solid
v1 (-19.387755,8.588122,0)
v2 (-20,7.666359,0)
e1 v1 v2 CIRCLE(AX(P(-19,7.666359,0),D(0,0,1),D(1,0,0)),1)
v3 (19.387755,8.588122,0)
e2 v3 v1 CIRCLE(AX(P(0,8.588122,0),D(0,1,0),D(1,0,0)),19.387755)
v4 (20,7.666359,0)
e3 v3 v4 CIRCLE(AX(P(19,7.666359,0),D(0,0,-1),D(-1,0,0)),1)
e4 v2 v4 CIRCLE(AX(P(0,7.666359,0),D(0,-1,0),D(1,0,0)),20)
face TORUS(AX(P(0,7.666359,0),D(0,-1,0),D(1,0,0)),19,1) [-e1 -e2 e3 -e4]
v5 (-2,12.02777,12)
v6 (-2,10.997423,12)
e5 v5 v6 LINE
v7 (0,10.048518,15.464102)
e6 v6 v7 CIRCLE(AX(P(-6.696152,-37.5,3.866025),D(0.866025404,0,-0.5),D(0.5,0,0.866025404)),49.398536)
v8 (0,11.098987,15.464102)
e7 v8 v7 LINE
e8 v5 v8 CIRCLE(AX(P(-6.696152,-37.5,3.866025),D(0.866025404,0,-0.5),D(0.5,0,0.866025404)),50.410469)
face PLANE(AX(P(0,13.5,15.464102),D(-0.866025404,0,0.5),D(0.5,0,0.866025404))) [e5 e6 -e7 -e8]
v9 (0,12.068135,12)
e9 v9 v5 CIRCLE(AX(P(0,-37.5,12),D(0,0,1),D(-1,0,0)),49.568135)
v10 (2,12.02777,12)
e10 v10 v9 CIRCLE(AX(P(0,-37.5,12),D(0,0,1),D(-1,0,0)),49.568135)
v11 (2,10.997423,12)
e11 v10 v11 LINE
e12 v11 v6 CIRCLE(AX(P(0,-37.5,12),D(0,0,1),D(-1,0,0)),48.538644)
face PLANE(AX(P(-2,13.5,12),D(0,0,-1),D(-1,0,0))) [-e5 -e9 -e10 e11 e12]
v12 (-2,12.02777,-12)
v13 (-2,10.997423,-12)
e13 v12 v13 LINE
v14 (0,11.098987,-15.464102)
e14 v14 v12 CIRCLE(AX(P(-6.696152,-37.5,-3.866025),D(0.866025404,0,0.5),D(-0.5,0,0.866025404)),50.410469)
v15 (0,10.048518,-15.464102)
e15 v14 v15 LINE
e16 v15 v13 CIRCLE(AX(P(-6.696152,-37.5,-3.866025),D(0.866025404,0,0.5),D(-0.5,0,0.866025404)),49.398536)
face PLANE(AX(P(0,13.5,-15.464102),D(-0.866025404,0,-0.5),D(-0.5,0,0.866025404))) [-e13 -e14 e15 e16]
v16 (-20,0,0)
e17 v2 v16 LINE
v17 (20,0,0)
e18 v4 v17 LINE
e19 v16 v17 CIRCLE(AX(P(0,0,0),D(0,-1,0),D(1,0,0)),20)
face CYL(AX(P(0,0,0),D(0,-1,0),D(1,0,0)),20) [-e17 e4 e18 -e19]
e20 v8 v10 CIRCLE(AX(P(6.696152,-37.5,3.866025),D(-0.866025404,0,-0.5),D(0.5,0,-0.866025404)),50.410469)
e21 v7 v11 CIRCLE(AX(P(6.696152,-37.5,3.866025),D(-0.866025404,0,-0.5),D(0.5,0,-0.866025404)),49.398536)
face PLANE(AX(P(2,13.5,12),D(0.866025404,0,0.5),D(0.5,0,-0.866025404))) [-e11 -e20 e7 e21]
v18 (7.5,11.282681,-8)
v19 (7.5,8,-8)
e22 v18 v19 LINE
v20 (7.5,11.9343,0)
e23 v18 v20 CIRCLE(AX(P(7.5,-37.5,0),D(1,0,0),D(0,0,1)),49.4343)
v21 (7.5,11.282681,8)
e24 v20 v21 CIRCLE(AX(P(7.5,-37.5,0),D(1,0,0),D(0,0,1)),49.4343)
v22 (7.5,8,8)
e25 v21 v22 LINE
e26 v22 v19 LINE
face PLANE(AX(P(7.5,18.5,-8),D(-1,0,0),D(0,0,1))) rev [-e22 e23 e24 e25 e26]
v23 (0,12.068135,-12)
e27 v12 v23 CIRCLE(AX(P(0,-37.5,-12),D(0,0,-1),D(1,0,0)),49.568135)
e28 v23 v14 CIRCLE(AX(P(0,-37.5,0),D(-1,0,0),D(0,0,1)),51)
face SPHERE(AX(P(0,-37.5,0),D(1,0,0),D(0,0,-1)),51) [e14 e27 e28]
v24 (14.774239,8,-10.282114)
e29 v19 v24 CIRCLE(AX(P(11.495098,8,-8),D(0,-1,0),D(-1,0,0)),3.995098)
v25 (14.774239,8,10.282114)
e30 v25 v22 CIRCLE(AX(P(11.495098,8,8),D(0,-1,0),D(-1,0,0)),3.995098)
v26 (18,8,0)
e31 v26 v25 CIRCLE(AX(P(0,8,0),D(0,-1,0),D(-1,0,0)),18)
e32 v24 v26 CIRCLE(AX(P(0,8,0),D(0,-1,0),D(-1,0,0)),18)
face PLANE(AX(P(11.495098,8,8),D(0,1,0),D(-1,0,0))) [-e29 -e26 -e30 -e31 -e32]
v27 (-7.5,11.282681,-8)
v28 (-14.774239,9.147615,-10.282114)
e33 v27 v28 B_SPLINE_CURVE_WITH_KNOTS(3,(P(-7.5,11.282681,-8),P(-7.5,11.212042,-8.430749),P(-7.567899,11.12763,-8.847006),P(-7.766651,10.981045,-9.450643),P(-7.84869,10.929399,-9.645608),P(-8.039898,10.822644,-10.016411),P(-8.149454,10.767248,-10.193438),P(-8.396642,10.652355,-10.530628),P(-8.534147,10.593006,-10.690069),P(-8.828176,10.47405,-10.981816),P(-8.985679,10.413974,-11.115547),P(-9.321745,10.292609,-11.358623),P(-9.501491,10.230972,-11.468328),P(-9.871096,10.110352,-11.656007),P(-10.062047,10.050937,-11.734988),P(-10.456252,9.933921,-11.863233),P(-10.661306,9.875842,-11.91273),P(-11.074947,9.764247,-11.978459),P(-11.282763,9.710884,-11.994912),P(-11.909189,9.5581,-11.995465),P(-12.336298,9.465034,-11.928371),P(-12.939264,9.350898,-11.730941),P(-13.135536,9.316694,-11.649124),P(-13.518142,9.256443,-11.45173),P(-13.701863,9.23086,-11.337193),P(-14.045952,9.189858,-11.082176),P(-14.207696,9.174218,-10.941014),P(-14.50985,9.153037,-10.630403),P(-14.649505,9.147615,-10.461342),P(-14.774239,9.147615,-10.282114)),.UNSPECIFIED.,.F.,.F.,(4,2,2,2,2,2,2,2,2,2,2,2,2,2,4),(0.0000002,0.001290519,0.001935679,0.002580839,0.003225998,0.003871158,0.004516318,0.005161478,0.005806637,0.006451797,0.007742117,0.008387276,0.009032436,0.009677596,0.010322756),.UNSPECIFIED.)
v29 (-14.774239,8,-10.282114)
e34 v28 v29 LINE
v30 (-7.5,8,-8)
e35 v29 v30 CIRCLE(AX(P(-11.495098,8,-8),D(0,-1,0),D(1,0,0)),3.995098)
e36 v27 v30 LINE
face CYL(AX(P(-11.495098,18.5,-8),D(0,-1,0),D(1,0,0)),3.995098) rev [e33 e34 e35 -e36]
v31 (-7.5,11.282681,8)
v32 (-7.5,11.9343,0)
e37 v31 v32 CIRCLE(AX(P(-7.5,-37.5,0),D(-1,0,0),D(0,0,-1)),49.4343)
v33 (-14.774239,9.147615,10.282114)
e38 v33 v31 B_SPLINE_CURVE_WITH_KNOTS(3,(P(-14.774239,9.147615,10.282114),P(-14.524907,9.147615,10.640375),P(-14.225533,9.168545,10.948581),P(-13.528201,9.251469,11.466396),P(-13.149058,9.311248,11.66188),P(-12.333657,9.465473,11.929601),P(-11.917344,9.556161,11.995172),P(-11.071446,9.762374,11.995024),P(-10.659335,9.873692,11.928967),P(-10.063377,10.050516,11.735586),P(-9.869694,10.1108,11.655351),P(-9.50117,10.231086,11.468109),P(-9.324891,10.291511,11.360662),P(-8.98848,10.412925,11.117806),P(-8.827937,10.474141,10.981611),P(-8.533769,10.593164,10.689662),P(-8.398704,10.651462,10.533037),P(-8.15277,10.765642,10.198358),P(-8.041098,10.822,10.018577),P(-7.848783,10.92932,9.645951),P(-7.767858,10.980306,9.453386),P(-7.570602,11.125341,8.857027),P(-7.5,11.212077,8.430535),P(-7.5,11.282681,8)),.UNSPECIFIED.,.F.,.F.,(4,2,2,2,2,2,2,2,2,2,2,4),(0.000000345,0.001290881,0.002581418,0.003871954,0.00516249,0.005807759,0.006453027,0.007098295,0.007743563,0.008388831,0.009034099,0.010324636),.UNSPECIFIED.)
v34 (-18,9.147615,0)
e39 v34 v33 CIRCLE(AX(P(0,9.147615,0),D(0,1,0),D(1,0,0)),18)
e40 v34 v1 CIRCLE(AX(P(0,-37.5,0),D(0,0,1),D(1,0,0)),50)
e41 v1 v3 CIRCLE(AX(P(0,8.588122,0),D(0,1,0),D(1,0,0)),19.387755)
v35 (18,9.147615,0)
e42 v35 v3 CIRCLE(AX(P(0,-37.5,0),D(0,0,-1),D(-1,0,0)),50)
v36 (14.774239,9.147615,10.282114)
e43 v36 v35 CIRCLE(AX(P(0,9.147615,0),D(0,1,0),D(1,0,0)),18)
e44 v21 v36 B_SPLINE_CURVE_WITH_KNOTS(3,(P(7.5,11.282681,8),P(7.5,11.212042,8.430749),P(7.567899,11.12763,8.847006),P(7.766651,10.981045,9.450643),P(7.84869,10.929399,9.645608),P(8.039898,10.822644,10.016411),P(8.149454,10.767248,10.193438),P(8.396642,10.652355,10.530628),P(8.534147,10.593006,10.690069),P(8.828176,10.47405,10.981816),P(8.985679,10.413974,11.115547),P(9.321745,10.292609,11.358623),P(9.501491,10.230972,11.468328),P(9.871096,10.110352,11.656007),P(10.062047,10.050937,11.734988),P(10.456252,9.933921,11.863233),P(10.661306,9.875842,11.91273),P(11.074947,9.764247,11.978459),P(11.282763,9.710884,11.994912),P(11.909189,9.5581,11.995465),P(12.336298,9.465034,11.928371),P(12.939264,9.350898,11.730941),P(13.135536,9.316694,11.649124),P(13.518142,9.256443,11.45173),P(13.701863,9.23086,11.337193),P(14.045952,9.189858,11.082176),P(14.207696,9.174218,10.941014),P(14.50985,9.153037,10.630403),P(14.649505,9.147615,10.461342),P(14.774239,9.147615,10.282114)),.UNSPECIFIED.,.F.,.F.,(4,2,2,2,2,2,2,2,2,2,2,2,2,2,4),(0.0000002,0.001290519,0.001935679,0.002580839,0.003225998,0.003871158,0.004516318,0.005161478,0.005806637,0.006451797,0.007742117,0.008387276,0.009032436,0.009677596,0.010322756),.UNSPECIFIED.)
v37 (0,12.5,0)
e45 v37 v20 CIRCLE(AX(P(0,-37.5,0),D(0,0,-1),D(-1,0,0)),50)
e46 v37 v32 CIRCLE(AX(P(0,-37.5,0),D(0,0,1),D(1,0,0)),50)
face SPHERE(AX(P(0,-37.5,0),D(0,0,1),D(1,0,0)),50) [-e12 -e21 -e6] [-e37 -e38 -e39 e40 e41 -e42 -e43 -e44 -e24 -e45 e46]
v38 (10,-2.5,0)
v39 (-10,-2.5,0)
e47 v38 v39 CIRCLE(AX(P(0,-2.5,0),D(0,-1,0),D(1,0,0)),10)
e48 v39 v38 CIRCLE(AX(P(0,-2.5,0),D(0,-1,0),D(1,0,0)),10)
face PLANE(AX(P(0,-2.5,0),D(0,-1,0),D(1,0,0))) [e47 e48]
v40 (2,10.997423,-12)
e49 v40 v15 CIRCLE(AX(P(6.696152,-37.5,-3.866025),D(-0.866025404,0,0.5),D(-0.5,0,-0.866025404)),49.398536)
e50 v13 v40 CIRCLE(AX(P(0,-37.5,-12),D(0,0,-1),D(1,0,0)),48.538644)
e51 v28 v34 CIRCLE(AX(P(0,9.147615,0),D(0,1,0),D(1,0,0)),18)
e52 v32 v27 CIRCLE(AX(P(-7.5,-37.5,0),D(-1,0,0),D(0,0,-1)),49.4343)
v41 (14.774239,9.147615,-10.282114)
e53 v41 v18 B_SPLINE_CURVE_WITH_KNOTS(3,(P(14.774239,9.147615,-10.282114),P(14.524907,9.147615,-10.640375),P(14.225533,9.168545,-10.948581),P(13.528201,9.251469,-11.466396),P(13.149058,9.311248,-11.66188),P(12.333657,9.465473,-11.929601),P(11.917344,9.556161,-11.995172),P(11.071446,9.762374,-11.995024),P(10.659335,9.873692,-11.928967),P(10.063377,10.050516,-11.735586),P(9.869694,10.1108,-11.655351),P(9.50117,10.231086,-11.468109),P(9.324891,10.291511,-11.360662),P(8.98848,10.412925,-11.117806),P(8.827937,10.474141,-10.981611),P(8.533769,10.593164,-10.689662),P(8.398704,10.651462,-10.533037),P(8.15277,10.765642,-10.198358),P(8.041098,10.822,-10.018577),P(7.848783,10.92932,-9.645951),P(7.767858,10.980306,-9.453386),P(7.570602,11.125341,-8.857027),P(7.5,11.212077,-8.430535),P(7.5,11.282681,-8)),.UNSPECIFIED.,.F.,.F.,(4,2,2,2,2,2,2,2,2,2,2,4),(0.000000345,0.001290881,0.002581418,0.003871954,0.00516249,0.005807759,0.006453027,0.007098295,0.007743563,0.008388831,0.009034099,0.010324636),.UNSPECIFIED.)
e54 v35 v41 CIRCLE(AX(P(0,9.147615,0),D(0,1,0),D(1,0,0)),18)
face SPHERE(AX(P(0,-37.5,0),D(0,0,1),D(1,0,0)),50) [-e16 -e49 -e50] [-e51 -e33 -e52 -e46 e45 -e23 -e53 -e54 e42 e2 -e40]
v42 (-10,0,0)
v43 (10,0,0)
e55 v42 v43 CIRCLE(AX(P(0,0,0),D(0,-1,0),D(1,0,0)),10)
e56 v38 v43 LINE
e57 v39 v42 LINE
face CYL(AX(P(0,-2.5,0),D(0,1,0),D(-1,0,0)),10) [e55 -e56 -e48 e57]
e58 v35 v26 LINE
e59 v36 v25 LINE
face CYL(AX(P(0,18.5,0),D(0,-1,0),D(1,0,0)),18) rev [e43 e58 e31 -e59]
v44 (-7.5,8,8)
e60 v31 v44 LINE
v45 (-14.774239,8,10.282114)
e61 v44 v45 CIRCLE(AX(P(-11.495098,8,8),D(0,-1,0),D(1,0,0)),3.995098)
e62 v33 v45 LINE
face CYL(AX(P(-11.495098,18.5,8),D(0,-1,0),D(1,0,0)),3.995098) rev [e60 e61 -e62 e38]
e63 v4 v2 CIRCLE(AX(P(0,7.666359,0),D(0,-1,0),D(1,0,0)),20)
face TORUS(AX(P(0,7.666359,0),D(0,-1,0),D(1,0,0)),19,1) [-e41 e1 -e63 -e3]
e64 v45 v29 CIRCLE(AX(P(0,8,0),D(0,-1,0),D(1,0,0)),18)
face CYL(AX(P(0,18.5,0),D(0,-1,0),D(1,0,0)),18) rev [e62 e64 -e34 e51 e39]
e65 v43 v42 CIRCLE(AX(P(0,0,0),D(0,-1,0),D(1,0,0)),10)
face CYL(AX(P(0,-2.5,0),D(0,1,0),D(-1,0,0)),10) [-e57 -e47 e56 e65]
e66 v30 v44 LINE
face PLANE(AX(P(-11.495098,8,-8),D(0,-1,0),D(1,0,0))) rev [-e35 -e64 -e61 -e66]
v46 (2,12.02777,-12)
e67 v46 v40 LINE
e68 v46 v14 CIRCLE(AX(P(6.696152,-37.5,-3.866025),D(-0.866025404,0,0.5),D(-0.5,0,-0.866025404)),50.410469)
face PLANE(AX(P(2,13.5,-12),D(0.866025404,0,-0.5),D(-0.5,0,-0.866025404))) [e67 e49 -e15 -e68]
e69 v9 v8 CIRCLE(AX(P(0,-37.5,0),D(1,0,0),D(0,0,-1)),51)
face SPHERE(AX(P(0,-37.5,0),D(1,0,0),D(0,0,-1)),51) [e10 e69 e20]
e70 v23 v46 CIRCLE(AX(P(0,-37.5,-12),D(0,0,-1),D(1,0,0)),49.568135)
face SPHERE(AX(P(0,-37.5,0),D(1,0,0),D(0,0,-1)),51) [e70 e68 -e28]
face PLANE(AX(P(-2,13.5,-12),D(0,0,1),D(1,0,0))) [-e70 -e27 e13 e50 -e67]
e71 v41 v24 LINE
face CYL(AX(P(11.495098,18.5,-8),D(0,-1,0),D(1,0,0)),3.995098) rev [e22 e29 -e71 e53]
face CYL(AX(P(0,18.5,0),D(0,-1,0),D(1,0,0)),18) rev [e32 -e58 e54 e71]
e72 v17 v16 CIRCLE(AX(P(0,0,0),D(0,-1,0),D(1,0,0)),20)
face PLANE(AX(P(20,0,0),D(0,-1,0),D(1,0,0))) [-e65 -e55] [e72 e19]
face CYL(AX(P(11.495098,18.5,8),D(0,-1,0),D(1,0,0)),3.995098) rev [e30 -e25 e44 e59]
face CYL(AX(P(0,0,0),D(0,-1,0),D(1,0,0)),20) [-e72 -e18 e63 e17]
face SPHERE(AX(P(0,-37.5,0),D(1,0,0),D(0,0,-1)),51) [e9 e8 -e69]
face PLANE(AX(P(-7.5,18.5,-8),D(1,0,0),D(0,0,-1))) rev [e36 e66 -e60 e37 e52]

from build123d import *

# Parameters (mm, degrees)
FILLET1_R           = 1
SKETCH2_R           = 10
BOSS_EXTRUDE1_DEPTH = 2.5
CUT_EXTRUDE1_DEPTH  = 10.5
BOSS_EXTRUDE2_DEPTH = 13.5


with BuildPart() as part:
    # Sketch1 → Revolve1 (revolve)
    with BuildSketch(Plane.XY):
        with BuildLine():
            Line((20, 8.32575695), (20, 0))
            Line((20, 0), (0, 0))
            Line((0, 0), (0, 12.5))
            ThreePointArc((0, 12.5), (10.215482184, 11.445315647), (20, 8.32575695))
        make_face()
    revolve(axis=Axis((0, 0, 0), (0, 1, 0)))

    # Fillet1
    fillet1_edges = [part.edges().sort_by_distance(p)[0] for p in [
        (-20, 8.32575695, 0),
    ]]
    fillet(fillet1_edges, radius=FILLET1_R)

    # Sketch2 → Boss-Extrude1 (add)
    with BuildSketch(Plane.XZ):
        Circle(SKETCH2_R)
    extrude(amount=BOSS_EXTRUDE1_DEPTH)

    # Sketch3 → Cut-Extrude1 (cut)
    with BuildSketch(Plane(origin=(0, 8, 0), x_dir=(-1, 0, 0), z_dir=(0, -1, 0))):
        with BuildLine():
            Line((7.5, 8), (7.5, -8))
            ThreePointArc((7.5, -8), (10.299205094, -11.811908762), (14.774238712, -10.282114106))
            ThreePointArc((14.774238712, -10.282114106), (18, 0), (14.774238712, 10.282114106))
            ThreePointArc((14.774238712, 10.282114106), (10.299205094, 11.811908762), (7.5, 8))
        make_face()
        with BuildLine():
            Line((-7.5, 8), (-7.5, -8))
            ThreePointArc((-7.5, -8), (-10.299205094, -11.811908762), (-14.774238712, -10.282114106))
            ThreePointArc((-14.774238712, -10.282114106), (-18, 0), (-14.774238712, 10.282114106))
            ThreePointArc((-14.774238712, 10.282114106), (-10.299205094, 11.811908762), (-7.5, 8))
        make_face()
    extrude(amount=-CUT_EXTRUDE1_DEPTH, mode=Mode.SUBTRACT)

    # Sketch5 → Boss-Extrude2 (add)
    with BuildSketch(Plane.XZ):
        Polygon((2, -12), (0, -15.464101615), (-2, -12), align=None)
        Polygon((2, 12), (0, 15.464101615), (-2, 12), align=None)
    extrude(amount=-BOSS_EXTRUDE2_DEPTH)

    # Sketch4 → Cut-Revolve3 (revolve, cut)
    with BuildSketch(Plane(origin=(0, 0, 0), x_dir=(0, 0, -1), z_dir=(1, 0, 0)), mode=Mode.PRIVATE) as cut_revolve3_sk:
        with BuildLine():
            Line((0, 17.5), (0, 13.5))
            ThreePointArc((0, 13.5), (9.805586606, 12.548481209), (19.245283019, 9.729430248))
            ThreePointArc((19.245283019, 9.729430248), (21.85213452, 10.826847786), (20.754716981, 13.433699287))
            ThreePointArc((20.754716981, 13.433699287), (10.574652222, 16.473852284), (0, 17.5))
        make_face()
    revolve(cut_revolve3_sk.sketch.rotate(Axis((0, 0, 0), (0, 1, 0)), 270), axis=Axis((0, 0, 0), (0, 1, 0)), mode=Mode.SUBTRACT)


solid = part.part
